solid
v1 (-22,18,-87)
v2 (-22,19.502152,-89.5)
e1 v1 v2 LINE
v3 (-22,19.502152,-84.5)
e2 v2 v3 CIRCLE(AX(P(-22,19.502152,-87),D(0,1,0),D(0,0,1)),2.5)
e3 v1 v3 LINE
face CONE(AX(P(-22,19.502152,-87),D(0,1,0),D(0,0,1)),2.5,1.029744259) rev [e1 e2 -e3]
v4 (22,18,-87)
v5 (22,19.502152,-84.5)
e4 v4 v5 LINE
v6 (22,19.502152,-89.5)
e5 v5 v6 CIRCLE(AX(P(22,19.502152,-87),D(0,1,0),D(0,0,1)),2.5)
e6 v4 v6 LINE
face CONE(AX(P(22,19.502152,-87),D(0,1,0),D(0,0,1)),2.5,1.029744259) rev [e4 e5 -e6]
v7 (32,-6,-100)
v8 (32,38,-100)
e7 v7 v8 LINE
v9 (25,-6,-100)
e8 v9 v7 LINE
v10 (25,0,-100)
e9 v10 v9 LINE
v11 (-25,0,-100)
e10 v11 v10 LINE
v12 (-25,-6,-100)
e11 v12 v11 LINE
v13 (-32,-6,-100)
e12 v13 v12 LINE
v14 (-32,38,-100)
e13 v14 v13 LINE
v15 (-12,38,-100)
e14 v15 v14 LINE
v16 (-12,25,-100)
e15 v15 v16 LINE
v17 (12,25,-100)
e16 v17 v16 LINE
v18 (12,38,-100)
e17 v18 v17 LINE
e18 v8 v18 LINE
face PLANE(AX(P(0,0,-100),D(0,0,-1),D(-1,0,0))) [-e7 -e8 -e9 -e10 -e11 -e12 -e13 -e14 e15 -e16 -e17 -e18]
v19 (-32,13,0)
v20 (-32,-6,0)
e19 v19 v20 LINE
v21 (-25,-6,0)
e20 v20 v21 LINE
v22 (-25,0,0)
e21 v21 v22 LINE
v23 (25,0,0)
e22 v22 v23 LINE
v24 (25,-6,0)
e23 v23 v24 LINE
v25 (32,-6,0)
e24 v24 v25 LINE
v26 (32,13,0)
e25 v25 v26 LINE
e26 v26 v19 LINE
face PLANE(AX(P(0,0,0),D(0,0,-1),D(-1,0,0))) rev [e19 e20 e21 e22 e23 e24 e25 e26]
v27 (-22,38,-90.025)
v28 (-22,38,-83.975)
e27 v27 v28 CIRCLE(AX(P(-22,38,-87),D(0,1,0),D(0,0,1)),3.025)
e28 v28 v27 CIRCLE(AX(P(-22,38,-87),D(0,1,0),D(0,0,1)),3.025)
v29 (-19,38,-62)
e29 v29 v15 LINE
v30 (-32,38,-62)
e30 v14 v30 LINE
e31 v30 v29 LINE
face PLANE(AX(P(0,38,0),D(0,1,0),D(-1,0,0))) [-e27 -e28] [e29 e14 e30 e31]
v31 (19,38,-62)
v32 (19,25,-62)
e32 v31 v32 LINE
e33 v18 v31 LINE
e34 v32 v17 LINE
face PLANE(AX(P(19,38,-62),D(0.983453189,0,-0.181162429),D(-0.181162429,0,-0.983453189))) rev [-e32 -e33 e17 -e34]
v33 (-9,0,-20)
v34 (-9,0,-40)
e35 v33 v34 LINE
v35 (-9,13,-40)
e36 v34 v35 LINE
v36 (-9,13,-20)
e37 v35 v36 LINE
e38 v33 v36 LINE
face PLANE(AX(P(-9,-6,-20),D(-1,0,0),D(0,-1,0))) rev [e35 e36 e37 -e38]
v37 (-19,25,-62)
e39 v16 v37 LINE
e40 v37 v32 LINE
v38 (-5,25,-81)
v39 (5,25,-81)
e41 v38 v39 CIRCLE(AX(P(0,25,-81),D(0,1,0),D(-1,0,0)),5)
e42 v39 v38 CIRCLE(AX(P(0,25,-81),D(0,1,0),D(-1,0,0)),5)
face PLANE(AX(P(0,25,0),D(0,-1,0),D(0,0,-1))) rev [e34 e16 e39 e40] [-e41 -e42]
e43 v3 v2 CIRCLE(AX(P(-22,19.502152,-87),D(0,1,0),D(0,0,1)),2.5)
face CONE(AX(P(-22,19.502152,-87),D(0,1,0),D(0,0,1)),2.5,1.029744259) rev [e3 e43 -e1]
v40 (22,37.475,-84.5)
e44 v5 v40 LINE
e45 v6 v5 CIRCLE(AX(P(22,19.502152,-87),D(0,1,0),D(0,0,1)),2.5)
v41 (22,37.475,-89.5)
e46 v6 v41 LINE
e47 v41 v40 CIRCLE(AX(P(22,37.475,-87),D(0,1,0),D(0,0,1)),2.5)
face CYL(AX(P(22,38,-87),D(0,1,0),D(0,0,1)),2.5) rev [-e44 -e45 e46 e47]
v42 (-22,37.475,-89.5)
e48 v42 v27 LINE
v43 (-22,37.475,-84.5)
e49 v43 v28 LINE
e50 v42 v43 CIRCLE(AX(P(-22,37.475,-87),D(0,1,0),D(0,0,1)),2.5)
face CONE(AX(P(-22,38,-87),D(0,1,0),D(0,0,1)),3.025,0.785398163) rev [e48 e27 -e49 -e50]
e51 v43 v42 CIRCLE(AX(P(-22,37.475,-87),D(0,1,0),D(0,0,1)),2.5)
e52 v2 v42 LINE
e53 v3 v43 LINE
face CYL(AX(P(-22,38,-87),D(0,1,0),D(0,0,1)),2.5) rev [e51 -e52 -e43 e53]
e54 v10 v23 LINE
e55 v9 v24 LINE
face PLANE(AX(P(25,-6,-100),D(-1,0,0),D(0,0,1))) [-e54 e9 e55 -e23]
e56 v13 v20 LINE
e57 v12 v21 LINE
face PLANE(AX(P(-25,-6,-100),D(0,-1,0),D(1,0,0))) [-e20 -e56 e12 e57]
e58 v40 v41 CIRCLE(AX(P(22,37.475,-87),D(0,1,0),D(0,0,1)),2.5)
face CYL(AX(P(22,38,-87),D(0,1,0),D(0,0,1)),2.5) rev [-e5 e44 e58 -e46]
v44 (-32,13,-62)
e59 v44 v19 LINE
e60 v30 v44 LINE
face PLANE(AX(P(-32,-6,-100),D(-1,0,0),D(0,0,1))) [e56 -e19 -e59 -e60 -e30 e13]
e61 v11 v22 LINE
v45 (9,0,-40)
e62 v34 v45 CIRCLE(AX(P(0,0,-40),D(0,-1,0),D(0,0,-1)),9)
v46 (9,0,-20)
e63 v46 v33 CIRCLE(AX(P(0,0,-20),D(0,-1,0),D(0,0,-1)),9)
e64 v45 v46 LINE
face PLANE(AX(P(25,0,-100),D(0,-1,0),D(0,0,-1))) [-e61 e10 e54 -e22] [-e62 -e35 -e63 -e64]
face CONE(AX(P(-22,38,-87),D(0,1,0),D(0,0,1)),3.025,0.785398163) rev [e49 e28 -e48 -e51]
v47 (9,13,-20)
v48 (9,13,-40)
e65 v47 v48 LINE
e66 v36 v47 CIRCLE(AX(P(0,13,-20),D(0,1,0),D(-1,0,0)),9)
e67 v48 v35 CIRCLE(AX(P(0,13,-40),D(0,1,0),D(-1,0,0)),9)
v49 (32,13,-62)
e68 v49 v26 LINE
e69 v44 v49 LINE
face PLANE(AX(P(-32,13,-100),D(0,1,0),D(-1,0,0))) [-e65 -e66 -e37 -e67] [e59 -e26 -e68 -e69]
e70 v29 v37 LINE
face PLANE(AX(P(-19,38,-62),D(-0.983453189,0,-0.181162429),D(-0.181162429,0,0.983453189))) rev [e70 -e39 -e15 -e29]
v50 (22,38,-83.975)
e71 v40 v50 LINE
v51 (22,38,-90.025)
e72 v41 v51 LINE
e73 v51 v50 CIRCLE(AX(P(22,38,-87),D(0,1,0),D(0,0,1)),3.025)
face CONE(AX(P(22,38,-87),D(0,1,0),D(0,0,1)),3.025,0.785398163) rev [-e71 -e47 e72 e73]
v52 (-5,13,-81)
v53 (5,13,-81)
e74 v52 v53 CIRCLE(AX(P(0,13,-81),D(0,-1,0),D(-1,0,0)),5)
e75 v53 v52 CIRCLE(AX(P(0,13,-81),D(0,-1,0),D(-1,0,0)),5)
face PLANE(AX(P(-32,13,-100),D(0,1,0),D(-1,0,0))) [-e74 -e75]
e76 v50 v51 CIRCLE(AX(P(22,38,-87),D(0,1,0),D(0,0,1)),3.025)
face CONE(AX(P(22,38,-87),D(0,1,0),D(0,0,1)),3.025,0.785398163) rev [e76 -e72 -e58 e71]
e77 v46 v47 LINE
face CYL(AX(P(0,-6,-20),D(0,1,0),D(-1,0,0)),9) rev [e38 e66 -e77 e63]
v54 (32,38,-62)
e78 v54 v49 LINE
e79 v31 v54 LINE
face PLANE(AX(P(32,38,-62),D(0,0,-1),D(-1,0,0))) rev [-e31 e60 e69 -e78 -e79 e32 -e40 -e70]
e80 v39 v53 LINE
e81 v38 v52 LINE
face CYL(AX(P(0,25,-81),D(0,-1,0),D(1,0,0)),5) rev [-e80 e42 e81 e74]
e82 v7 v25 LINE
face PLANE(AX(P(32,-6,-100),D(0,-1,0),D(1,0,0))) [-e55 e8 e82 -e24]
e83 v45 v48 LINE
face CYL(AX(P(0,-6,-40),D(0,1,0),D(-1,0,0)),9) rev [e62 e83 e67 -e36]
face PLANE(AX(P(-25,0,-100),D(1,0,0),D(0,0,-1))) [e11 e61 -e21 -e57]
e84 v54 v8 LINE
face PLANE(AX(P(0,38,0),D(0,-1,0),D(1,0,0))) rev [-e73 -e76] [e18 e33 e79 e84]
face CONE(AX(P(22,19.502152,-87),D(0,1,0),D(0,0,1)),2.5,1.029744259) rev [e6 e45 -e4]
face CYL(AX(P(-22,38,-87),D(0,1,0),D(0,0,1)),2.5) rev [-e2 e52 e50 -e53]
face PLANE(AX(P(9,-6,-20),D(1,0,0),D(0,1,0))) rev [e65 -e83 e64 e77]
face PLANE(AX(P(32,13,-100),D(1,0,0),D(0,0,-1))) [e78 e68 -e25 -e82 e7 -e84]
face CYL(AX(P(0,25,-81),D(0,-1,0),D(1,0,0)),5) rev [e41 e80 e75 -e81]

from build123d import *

# Parameters (mm, degrees)
BASE_PLATE_DEPTH                      = 100
V_BLOCK_UPRIGHTS_DEPTH                = 25
M6_TAPPED_HOLES_2X_D                  = 5
M6_TAPPED_HOLES_2X_DEPTH              = 18.497848452
M6_TAPPED_HOLES_2X_CSINK_D            = 6.05
M6_TAPPED_HOLES_2X_CSINK_ANGLE        = 90
M6_TAPPED_HOLES_2X_TIP                = 1.502151548
CENTRE_STEP_BLOCK_PROFILE_R           = 5
CENTRE_STEP_BLOCK_DEPTH               = 12
ADJUSTMENT_SLOT_AND_CENTRE_HOLE_DEPTH = 108.930533215


with BuildPart() as part:
    # Base Plate Profile → Base Plate (new body)
    with BuildSketch(Plane.XY):
        Polygon((25, 0), (-25, 0), (-25, -6), (-32, -6), (-32, 13), (32, 13), (32, -6), (25, -6), align=None)
    extrude(amount=-BASE_PLATE_DEPTH)

    # V-Block Uprights Profile → V-Block Uprights (add)
    with BuildSketch(Plane(origin=(0, 13, 0), x_dir=(1, 0, 0), z_dir=(0, 1, 0))):
        Polygon((32, 100), (32, 62), (19, 62), (12, 100), align=None)
        Polygon((-12, 100), (-32, 100), (-32, 62), (-19, 62), align=None)
    extrude(amount=V_BLOCK_UPRIGHTS_DEPTH)

    # M6 Tapped Holes 2x
    with Locations(Plane(origin=(0, 38, 0), x_dir=(1, 0, 0), z_dir=(0, 1, 0))):
        with Locations((22, 87), (-22, 87)):
            CounterSinkHole(M6_TAPPED_HOLES_2X_D / 2, M6_TAPPED_HOLES_2X_CSINK_D / 2, depth=M6_TAPPED_HOLES_2X_DEPTH, counter_sink_angle=M6_TAPPED_HOLES_2X_CSINK_ANGLE)
            with Locations((0, 0, -(M6_TAPPED_HOLES_2X_DEPTH + M6_TAPPED_HOLES_2X_TIP / 2))):  # 118° drill point
                Cone(0, M6_TAPPED_HOLES_2X_D / 2, M6_TAPPED_HOLES_2X_TIP, mode=Mode.SUBTRACT)

    # Centre Step Block Profile → Centre Step Block (add)
    with BuildSketch(Plane(origin=(0, 13, 0), x_dir=(1, 0, 0), z_dir=(0, 1, 0))):
        Polygon((-12, 100), (12, 100), (19, 62), (-19, 62), align=None)
        with Locations(Location((0, 81, 0), (0, 0, 180))):
            Circle(CENTRE_STEP_BLOCK_PROFILE_R, mode=Mode.SUBTRACT)
    extrude(amount=CENTRE_STEP_BLOCK_DEPTH)

    # Adjustment Slot and Centre Hole Profile → Adjustment Slot and Centre Hole (cut, through all)
    with BuildSketch(Plane(origin=(0, 13, 0), x_dir=(1, 0, 0), z_dir=(0, 1, 0))):
        with BuildLine():
            Line((-9, 20), (-9, 40))
            ThreePointArc((-9, 40), (0, 49), (9, 40))
            Line((9, 40), (9, 20))
            ThreePointArc((9, 20), (0, 11), (-9, 20))
        make_face()
    extrude(amount=-ADJUSTMENT_SLOT_AND_CENTRE_HOLE_DEPTH, mode=Mode.SUBTRACT)


solid = part.part
